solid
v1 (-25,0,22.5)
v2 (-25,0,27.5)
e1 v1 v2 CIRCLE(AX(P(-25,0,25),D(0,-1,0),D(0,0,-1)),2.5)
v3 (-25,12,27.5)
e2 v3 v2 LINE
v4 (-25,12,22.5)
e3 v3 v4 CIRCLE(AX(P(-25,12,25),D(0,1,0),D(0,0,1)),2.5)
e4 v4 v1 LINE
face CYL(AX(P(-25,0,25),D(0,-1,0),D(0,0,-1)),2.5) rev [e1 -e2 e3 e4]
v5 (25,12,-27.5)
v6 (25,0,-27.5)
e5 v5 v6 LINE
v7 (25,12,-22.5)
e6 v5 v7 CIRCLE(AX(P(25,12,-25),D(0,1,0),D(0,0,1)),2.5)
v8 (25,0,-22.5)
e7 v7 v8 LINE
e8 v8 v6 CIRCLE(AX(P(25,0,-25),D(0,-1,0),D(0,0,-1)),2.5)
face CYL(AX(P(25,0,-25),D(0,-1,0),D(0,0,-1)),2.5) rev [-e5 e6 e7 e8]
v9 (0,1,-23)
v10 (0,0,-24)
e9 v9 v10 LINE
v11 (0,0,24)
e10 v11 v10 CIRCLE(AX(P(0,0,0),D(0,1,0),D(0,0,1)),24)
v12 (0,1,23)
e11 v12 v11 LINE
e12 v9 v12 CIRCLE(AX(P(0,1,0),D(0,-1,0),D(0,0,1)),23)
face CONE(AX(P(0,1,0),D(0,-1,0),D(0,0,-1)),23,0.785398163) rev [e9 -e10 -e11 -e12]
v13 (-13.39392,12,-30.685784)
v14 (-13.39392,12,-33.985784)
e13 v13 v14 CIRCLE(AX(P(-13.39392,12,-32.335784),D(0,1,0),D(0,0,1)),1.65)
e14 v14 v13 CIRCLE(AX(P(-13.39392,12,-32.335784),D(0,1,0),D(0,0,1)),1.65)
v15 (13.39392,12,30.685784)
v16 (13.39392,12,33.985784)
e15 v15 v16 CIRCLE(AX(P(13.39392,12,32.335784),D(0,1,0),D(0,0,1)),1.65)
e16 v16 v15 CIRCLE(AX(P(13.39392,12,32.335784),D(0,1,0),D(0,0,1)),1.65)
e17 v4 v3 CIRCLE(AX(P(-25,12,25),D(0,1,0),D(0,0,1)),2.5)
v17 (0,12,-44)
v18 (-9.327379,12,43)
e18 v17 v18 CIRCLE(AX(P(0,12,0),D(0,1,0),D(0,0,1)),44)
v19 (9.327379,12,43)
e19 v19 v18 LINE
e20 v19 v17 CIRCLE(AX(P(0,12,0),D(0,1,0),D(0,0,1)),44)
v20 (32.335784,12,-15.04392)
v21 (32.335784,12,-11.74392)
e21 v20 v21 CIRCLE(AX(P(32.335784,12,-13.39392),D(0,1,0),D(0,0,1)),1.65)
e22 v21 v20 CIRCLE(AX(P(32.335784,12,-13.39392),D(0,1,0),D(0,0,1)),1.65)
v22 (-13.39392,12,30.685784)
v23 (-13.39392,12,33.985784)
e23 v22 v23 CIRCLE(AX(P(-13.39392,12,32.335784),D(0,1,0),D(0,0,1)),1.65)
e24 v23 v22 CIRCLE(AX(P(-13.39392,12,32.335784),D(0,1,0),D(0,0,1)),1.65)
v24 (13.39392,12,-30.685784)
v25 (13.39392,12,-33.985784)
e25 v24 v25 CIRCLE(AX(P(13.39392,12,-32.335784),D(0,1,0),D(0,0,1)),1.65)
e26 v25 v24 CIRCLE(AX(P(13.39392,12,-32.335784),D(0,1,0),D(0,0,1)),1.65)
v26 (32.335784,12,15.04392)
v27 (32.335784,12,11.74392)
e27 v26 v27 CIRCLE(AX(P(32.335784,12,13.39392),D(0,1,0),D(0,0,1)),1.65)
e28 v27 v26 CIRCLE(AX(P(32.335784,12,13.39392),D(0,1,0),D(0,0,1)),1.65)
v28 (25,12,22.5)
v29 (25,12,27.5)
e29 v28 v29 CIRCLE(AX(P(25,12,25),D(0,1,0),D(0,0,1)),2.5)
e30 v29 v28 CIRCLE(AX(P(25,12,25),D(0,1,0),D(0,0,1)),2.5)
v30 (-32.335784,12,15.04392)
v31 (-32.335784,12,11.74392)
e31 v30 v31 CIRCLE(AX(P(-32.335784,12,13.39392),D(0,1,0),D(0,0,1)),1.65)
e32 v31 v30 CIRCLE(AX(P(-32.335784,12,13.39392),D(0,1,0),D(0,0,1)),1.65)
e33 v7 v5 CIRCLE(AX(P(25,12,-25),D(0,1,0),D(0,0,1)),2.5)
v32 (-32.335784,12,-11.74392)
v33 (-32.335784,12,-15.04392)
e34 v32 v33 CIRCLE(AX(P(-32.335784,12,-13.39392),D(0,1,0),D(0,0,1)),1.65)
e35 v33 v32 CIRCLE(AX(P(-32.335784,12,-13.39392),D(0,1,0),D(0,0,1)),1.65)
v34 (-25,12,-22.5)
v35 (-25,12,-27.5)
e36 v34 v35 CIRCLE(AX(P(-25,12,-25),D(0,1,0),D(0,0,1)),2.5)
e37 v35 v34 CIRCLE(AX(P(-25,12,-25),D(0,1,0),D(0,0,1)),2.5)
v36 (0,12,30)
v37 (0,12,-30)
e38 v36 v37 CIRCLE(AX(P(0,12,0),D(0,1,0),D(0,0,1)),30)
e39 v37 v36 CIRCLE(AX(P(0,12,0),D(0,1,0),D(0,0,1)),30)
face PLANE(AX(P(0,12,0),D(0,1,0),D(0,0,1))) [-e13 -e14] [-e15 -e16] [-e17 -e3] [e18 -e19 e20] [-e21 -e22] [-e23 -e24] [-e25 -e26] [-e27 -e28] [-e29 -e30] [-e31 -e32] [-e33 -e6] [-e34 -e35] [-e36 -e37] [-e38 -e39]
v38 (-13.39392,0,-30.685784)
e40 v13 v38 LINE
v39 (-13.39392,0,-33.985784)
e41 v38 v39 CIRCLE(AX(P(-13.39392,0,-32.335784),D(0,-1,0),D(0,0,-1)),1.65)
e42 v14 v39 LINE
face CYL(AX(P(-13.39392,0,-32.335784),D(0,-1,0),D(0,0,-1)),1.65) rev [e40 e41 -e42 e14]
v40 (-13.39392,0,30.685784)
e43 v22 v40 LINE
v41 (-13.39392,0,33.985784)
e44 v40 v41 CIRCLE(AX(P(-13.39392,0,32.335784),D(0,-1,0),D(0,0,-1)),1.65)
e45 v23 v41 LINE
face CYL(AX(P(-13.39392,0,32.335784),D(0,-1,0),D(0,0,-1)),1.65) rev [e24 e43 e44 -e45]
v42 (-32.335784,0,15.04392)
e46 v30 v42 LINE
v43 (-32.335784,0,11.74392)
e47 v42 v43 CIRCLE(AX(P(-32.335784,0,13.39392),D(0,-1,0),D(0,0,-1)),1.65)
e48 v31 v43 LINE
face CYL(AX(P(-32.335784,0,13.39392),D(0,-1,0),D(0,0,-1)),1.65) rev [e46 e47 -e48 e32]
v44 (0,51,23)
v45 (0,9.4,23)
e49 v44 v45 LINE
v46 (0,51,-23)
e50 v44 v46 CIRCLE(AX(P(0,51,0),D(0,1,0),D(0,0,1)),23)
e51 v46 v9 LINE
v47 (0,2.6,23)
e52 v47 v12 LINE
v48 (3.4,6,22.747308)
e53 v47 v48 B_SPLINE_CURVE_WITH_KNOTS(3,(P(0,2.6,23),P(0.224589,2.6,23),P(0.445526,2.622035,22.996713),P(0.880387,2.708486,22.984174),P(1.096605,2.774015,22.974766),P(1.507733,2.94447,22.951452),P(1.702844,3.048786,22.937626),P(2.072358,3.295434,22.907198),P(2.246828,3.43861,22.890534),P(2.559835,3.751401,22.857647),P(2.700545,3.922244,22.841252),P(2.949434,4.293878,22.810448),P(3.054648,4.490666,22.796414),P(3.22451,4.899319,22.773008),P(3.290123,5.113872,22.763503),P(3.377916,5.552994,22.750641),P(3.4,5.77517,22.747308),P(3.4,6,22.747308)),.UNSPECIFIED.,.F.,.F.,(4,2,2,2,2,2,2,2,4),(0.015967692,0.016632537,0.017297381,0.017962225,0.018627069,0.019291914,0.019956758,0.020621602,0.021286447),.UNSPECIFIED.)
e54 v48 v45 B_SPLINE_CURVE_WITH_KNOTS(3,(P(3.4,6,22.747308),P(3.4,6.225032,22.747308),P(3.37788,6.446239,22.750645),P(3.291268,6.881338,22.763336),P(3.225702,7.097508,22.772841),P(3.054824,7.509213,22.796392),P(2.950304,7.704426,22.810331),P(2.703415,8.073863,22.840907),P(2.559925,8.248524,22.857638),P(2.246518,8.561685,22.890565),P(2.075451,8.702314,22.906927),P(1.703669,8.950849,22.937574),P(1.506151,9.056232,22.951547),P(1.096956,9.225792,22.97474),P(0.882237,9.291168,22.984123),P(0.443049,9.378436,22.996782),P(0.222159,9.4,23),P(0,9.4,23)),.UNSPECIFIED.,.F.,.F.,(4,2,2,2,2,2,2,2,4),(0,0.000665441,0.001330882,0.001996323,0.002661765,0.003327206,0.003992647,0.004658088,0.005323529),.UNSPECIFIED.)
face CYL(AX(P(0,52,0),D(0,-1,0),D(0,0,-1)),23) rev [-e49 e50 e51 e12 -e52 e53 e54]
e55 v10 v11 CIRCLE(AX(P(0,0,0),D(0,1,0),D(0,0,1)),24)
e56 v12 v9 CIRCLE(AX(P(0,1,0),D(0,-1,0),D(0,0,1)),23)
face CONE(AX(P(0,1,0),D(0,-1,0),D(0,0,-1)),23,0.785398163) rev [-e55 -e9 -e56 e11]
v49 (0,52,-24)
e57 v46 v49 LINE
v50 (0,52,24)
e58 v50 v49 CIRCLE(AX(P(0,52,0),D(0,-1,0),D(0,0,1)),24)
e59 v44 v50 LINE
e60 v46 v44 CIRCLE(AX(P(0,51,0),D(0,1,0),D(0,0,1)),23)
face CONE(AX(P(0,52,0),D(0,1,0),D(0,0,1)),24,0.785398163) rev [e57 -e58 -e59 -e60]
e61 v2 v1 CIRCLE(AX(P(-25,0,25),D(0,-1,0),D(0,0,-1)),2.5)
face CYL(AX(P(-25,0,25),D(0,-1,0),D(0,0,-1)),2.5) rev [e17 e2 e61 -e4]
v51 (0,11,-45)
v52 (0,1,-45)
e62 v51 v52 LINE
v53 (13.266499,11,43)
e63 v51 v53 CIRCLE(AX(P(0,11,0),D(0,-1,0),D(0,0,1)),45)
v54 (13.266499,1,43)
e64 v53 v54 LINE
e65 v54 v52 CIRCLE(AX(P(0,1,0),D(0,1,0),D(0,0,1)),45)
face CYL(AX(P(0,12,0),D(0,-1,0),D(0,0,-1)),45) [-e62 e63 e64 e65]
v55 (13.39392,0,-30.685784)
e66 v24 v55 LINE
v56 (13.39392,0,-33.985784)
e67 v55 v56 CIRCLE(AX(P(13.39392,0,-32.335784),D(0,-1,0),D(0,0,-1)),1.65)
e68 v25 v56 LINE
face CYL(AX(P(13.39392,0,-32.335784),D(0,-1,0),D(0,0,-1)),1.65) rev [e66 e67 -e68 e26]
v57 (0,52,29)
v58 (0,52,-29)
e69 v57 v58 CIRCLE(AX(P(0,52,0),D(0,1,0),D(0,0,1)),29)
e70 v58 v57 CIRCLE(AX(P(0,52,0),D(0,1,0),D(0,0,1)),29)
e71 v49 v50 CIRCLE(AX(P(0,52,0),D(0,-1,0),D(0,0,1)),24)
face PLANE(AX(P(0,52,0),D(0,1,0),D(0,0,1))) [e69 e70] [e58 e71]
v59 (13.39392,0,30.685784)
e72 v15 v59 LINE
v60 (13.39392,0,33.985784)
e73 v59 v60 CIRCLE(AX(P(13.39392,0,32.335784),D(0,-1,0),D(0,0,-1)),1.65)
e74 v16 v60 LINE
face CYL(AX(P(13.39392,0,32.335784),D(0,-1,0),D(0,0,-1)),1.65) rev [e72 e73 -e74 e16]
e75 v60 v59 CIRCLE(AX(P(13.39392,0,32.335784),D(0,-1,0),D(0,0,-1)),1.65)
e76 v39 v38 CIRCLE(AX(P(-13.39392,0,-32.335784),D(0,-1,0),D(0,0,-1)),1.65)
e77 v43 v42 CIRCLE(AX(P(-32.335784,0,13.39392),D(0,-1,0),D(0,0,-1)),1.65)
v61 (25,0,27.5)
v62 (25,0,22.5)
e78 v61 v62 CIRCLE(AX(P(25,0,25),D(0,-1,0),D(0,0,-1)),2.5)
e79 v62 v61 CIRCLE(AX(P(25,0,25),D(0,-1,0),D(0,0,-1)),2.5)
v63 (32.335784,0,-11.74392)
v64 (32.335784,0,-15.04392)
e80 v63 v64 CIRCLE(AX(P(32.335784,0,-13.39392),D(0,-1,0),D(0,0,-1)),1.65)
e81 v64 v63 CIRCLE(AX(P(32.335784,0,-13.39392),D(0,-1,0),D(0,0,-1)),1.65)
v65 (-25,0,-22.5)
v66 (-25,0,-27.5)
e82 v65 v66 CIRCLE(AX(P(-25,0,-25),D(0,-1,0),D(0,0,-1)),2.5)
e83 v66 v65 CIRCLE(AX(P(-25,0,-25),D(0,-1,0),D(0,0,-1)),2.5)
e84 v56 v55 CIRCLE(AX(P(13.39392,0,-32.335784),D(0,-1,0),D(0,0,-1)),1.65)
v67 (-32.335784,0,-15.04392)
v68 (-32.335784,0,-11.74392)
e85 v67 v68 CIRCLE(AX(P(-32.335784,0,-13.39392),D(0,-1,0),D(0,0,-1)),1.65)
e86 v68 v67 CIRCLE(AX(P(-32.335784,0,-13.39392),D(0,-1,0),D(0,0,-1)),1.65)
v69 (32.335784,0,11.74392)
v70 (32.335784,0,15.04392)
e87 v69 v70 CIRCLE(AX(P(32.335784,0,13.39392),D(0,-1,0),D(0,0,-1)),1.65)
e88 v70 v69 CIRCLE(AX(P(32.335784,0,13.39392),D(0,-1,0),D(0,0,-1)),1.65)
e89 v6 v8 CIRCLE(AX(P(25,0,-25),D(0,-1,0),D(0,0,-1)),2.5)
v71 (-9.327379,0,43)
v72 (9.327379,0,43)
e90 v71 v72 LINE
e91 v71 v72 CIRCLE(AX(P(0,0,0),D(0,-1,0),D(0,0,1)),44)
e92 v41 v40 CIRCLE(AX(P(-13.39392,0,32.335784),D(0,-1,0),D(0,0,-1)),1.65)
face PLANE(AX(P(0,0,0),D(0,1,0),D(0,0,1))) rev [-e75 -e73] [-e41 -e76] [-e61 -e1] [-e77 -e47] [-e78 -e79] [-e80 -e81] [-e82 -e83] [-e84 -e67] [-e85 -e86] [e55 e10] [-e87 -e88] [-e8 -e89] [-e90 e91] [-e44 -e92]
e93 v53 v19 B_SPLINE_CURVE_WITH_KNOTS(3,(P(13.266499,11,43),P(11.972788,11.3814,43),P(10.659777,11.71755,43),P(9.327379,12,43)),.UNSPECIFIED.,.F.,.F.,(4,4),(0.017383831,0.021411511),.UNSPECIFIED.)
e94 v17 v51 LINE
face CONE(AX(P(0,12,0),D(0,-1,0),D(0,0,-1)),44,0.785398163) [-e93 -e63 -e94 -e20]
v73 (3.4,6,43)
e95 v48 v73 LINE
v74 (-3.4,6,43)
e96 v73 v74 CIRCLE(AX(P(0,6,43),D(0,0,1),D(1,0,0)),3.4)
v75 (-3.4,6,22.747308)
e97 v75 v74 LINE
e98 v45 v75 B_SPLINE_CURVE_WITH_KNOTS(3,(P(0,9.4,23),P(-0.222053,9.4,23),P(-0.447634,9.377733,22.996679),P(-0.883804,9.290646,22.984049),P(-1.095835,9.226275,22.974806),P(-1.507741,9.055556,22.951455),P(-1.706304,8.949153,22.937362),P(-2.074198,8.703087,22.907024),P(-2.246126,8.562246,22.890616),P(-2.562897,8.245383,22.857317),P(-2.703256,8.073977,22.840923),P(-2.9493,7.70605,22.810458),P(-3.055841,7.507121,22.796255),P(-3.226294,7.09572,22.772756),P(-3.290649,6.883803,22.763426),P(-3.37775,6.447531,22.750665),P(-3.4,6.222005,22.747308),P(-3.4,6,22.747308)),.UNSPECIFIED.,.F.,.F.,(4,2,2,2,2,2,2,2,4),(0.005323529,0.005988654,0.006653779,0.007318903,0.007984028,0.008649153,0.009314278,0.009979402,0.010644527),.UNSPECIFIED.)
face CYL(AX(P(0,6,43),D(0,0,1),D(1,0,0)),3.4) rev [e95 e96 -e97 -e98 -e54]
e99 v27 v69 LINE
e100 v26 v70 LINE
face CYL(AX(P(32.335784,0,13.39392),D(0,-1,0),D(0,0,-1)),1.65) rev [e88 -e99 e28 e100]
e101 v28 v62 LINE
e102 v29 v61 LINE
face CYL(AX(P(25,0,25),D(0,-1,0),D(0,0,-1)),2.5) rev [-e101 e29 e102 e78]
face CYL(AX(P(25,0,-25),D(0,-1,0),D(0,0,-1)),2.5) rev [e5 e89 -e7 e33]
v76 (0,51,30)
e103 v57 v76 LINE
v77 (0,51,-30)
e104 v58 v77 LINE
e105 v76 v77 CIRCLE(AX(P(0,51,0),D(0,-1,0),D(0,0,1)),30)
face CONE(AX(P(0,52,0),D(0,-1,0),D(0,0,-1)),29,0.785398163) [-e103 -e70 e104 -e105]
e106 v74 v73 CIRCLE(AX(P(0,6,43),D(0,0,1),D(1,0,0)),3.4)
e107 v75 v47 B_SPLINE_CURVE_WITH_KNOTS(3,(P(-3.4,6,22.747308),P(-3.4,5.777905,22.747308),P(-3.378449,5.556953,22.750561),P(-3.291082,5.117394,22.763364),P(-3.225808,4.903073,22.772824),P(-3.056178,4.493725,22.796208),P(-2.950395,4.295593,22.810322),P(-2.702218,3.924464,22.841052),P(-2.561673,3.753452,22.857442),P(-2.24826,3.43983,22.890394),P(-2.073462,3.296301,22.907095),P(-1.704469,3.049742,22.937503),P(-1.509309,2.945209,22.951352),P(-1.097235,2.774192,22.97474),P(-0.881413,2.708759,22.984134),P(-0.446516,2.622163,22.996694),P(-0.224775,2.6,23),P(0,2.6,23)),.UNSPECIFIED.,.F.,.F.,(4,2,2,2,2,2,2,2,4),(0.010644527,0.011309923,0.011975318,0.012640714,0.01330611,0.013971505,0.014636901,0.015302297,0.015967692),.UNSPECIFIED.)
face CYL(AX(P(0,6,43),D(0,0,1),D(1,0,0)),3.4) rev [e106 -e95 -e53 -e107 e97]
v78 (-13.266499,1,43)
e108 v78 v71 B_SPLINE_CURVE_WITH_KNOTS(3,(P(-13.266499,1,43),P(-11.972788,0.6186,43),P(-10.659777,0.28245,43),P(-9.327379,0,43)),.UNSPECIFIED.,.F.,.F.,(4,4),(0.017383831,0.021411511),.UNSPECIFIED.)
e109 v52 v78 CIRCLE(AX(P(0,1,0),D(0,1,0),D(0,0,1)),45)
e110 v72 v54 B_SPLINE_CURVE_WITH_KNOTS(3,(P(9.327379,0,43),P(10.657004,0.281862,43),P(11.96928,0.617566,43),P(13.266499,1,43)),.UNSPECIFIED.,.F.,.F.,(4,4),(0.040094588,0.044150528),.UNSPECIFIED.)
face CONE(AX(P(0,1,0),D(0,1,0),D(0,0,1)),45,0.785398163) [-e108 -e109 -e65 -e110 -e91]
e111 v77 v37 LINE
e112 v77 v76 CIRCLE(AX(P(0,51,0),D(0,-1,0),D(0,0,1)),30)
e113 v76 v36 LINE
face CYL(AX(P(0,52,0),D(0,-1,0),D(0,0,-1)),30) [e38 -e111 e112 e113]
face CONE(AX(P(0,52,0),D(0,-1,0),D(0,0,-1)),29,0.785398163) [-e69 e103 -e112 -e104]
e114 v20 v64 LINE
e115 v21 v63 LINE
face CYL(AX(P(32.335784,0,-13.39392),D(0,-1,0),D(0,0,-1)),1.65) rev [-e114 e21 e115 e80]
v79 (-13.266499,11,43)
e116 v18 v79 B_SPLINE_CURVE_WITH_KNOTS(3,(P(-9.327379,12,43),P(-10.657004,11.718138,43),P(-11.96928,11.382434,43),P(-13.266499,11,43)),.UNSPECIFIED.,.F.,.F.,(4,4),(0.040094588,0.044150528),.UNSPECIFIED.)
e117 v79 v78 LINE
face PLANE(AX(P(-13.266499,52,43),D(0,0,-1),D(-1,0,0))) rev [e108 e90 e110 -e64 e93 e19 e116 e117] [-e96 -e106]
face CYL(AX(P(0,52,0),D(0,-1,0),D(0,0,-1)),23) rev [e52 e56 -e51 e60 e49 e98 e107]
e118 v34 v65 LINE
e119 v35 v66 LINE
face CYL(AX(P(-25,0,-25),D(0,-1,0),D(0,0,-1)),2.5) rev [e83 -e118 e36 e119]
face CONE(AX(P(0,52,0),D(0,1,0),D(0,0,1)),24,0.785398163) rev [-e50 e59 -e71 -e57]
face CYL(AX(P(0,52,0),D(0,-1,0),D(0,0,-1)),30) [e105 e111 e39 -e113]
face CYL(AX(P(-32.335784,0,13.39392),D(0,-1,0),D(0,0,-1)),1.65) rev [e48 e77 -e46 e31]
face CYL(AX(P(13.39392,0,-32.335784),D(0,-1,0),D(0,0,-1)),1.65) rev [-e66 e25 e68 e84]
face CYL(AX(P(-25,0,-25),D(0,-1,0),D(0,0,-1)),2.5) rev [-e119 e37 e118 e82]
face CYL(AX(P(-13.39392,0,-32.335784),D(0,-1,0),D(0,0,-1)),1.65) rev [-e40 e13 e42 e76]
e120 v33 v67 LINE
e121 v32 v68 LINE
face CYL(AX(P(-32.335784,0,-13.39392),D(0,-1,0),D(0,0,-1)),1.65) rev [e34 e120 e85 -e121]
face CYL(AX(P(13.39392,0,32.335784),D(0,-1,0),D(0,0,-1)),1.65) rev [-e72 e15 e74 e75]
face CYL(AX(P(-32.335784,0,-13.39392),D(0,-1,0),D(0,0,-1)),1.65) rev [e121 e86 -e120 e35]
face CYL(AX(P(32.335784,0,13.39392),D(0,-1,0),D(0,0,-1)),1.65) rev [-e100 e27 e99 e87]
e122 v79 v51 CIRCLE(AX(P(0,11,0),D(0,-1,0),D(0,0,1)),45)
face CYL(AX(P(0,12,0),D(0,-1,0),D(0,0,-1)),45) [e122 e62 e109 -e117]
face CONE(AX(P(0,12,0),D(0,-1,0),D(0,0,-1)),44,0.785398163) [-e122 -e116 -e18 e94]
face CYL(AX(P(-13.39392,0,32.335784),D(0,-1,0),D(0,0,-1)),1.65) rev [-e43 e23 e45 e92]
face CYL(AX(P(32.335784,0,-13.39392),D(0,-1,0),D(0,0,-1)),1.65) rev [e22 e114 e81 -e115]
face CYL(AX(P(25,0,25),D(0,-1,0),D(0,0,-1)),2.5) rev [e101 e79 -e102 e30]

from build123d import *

# Parameters (mm, degrees)
SKETCH1_R              = 45
BOSS_EXTRUDE1_DEPTH    = 12
SKETCH2_R              = 30
BOSS_EXTRUDE2_DEPTH    = 40
SKETCH3_R              = 23
CUT_EXTRUDE1_DEPTH     = 83.182723245
CHAMFER1_SIZE          = 1
M6_TAPPED_HOLE1_D      = 5
M4_TAPPED_HOLE1_D      = 3.3
CUT_EXTRUDE2_DEPTH     = 83.182723245
CIRPATTERN1_COUNT      = 8
M8_TAPPED_HOLE1_REACH  = 113.683
M8_TAPPED_HOLE1_BORE_R = 3.4


with BuildPart() as part:
    # Sketch1 → Boss-Extrude1 (new body)
    with BuildSketch(Plane(origin=(0, 0, 0), x_dir=(1, 0, 0), z_dir=(0, 1, 0))):
        with Locations(Location((0, 0, 0), (0, 0, 270))):
            Circle(SKETCH1_R)
    extrude(amount=BOSS_EXTRUDE1_DEPTH)

    # Sketch2 → Boss-Extrude2 (add)
    with BuildSketch(Plane(origin=(0, 12, 0), x_dir=(1, 0, 0), z_dir=(0, 1, 0))):
        with Locations(Location((0, 0, 0), (0, 0, 270))):
            Circle(SKETCH2_R)
    extrude(amount=BOSS_EXTRUDE2_DEPTH)

    # Sketch3 → Cut-Extrude1 (cut, through all)
    with BuildSketch(Plane.XZ):
        with Locations(Location((0, 0, 0), (0, 0, 270))):
            Circle(SKETCH3_R)
    extrude(amount=-CUT_EXTRUDE1_DEPTH, mode=Mode.SUBTRACT)

    # Chamfer1
    chamfer1_edges = [part.edges().sort_by_distance(p)[0] for p in [
        (0, 52, 23),
        (0, 0, 23),
        (0, 0, -45),
        (0, 12, -45),
        (0, 52, -30),
    ]]
    chamfer(chamfer1_edges, length=CHAMFER1_SIZE)

    # M6 Tapped Hole1 (through all)
    with Locations(Plane(origin=(0, 0, 0), x_dir=(-1, 0, 0), z_dir=(0, -1, 0))):
        with Locations((25, -25), (-25, -25), (-25, 25), (25, 25)):
            Hole(M6_TAPPED_HOLE1_D / 2)

    # M4 Tapped Hole1 (through all)
    with Locations(Plane(origin=(0, 0, 0), x_dir=(-1, 0, 0), z_dir=(0, -1, 0))):
        with Locations((13.393920133, -32.335783638)):
            m4_tapped_hole1 = Hole(M4_TAPPED_HOLE1_D / 2)

    # Sketch8 → Cut-Extrude2 (cut, through all)
    with BuildSketch(Plane.XZ):
        with BuildLine():
            Line((-13.266499161, 43), (13.266499161, 43))
            ThreePointArc((13.266499161, 43), (0, 45), (-13.266499161, 43))
        make_face()
    extrude(amount=-CUT_EXTRUDE2_DEPTH, mode=Mode.SUBTRACT)

    # CirPattern1: M4 Tapped Hole1 ×8 about axis
    cirpattern1_axis = Axis((0, 0, 0), (0, 1, 0))
    for i in range(1, CIRPATTERN1_COUNT):
        add(m4_tapped_hole1.rotate(cirpattern1_axis, i * 360 / CIRPATTERN1_COUNT), mode=Mode.SUBTRACT)

    # M8 Tapped Hole1 bore → M8 Tapped Hole1 (cut, up to next)
    with BuildSketch(Plane.XY.offset(43), mode=Mode.PRIVATE) as m8_tapped_hole1_sk1:
        with Locations((0, 6)):
            Circle(M8_TAPPED_HOLE1_BORE_R)
    m8_tapped_hole1_tool1 = extrude(m8_tapped_hole1_sk1.sketch, amount=-M8_TAPPED_HOLE1_REACH, mode=Mode.PRIVATE) & part.part
    add(m8_tapped_hole1_tool1.solids().sort_by_distance((0, 6, 43))[0], mode=Mode.SUBTRACT)


solid = part.part
